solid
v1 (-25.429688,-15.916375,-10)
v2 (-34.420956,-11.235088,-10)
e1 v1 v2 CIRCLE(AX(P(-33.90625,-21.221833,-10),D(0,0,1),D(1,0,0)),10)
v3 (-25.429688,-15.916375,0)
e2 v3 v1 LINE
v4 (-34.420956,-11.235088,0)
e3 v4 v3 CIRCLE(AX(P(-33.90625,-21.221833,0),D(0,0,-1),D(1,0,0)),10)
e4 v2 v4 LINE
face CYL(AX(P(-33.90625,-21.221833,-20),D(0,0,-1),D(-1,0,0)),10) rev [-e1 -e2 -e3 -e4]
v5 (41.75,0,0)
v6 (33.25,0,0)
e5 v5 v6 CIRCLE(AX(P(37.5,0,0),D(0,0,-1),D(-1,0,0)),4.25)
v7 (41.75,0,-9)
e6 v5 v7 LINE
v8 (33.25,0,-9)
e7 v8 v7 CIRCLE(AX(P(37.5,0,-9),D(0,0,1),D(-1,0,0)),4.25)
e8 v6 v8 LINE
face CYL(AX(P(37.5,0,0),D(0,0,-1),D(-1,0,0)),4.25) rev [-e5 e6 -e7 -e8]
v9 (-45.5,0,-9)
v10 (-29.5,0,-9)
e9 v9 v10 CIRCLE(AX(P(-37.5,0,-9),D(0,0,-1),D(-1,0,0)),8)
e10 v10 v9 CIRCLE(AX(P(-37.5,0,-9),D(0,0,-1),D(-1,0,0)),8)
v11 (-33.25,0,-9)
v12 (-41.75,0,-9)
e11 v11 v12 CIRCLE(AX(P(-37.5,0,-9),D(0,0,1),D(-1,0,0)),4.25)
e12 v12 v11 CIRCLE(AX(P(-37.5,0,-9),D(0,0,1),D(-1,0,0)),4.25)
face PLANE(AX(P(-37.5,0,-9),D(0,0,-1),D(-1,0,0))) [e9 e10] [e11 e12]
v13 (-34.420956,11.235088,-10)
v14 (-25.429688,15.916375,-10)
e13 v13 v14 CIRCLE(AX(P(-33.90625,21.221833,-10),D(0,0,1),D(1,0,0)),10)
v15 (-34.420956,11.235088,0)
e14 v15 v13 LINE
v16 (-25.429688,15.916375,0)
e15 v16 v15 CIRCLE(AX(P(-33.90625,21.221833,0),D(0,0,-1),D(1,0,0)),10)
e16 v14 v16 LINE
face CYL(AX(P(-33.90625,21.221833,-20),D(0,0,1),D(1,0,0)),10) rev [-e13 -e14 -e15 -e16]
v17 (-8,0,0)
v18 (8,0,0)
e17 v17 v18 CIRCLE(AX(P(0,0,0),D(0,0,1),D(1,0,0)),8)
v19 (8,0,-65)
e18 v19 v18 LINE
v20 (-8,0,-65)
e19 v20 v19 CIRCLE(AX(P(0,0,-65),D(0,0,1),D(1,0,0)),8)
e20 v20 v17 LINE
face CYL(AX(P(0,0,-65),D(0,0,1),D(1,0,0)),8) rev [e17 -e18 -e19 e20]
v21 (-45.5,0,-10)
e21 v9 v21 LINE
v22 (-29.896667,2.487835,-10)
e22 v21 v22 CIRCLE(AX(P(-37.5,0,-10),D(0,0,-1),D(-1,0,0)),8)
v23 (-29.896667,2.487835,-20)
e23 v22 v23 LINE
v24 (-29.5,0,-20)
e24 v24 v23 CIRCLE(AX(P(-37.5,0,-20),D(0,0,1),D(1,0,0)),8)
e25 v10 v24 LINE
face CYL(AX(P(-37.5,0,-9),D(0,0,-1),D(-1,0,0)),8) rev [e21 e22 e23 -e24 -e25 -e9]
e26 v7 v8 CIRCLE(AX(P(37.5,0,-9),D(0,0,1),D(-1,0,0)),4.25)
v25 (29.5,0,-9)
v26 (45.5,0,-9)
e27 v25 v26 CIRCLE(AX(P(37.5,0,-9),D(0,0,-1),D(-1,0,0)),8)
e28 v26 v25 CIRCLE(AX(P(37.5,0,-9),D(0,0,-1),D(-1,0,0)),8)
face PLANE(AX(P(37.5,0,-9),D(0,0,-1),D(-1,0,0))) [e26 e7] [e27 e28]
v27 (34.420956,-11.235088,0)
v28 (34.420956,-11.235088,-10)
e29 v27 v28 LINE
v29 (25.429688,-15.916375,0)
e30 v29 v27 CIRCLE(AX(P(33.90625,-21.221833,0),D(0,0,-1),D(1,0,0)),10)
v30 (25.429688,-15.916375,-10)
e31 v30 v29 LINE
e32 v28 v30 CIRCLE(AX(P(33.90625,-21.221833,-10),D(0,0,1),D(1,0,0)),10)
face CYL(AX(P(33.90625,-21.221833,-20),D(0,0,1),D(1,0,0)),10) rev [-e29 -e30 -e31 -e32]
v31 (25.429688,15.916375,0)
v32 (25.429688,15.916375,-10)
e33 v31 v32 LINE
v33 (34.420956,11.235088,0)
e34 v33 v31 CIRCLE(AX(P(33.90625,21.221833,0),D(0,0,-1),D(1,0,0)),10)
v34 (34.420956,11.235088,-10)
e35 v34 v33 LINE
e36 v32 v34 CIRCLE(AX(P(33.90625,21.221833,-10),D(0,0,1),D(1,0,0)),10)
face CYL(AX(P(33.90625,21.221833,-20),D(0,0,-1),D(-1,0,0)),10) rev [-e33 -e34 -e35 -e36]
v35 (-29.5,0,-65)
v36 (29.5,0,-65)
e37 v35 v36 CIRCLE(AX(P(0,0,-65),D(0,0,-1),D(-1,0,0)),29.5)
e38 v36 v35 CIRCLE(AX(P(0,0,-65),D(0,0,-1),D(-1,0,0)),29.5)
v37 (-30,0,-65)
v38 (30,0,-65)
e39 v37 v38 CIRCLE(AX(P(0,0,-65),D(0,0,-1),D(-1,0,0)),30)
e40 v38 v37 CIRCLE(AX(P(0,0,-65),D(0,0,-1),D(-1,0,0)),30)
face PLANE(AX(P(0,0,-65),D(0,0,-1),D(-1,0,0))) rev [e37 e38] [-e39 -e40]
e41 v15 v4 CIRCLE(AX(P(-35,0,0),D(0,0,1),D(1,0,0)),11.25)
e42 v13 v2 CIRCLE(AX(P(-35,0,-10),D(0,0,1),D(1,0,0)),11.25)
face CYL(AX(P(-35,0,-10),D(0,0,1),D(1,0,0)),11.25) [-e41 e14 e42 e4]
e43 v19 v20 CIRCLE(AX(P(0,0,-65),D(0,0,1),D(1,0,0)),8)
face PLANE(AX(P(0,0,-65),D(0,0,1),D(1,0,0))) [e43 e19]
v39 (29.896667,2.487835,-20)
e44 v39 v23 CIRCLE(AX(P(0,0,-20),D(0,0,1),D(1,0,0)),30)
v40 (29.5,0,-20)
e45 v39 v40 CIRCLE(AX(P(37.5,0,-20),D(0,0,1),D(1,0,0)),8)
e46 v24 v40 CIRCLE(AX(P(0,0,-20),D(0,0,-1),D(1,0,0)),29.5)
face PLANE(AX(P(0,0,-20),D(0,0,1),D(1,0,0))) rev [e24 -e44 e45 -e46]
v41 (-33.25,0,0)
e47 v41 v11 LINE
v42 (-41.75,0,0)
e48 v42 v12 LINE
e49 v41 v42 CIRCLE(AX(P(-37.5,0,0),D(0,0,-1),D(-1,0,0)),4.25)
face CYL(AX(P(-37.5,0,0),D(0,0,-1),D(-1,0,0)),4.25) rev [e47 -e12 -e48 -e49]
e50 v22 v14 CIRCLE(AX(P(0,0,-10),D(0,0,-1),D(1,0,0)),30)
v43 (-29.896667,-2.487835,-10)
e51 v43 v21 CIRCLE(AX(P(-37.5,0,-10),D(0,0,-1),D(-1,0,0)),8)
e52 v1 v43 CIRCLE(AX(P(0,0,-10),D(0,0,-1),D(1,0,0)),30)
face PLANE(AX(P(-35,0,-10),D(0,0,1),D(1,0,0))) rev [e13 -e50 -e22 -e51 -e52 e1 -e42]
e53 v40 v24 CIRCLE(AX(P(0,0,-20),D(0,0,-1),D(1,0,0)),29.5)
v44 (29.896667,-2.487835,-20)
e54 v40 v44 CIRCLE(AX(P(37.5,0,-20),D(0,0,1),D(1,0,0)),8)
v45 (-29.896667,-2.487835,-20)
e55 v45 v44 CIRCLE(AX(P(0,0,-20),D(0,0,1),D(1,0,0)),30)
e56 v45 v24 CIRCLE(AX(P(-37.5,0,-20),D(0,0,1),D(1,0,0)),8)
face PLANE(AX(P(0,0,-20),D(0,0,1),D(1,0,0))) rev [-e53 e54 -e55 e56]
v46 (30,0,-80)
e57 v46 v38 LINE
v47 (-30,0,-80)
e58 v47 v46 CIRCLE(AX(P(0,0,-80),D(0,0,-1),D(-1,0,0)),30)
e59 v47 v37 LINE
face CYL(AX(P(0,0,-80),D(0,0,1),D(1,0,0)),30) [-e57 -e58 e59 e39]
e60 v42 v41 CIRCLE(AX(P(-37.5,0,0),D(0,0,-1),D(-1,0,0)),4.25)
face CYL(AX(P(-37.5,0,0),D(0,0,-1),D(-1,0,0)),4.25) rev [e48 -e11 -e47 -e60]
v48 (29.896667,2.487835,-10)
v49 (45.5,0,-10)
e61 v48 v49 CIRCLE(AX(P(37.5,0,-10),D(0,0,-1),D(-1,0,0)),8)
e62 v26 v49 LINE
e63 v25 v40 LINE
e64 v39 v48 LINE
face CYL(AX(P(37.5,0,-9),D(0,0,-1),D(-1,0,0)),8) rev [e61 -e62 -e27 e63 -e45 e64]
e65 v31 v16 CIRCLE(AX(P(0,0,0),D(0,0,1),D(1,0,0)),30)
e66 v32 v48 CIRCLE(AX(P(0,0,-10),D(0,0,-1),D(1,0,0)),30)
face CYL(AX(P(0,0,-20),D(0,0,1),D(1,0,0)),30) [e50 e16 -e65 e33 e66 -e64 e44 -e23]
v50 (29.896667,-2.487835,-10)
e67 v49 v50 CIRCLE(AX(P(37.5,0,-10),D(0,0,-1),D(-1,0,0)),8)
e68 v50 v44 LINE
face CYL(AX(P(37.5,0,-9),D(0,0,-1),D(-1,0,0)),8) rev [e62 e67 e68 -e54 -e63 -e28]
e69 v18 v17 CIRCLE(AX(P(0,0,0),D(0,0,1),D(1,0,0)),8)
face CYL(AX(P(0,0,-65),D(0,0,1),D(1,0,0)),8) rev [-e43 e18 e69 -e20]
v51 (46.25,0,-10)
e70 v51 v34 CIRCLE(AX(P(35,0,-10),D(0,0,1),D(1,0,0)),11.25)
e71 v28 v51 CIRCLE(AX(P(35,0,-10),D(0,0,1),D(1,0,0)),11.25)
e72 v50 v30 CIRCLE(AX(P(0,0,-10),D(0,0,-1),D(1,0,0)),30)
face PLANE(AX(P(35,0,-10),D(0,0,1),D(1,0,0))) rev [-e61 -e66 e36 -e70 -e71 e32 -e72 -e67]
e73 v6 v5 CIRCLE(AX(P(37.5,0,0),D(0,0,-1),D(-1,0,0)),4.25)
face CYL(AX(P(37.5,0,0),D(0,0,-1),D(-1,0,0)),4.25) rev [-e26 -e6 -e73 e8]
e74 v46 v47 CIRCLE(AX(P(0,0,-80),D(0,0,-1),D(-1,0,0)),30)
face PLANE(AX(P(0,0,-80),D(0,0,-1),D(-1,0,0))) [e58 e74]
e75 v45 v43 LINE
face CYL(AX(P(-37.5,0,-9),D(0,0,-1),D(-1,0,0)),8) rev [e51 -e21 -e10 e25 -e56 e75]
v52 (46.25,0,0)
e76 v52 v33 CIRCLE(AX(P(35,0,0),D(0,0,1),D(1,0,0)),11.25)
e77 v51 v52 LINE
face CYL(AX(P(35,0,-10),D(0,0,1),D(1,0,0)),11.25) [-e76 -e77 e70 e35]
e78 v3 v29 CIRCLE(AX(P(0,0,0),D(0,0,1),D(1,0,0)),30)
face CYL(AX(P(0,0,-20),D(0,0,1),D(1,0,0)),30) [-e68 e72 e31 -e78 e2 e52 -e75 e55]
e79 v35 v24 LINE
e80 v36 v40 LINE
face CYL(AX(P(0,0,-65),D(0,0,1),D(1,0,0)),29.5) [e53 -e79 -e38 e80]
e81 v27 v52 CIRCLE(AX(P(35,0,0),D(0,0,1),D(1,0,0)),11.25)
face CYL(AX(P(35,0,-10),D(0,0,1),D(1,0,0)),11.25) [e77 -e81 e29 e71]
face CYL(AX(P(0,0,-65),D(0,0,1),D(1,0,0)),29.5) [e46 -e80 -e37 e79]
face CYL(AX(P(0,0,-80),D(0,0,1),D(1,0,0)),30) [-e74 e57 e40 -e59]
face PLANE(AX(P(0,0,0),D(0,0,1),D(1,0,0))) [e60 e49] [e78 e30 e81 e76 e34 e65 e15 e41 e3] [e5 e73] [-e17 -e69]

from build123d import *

# Parameters (mm, degrees)
SKETCH1_R           = 30
BOSS_EXTRUDE1_DEPTH = 20
SKETCH2_R           = 29.5
BOSS_EXTRUDE2_DEPTH = 45
SKETCH3_R           = 30
BOSS_EXTRUDE3_DEPTH = 15
SKETCH4_R           = 8
CUT_EXTRUDE1_DEPTH  = 65
SKETCH5_R           = 11.25
BOSS_EXTRUDE4_DEPTH = 10
FILLET1_R           = 10
SKETCH6_R           = 4.25
CUT_EXTRUDE2_DEPTH  = 90.101417022
SKETCH_7_2_R        = 8
CUT_EXTRUDE3_DEPTH  = 1
CUT_EXTRUDE4_REACH  = 91.101
SKETCH_7_2_2_R      = 8


with BuildPart() as part:
    # Sketch1 → Boss-Extrude1 (new body)
    with BuildSketch(Plane.XY):
        Circle(SKETCH1_R)
    extrude(amount=-BOSS_EXTRUDE1_DEPTH)

    # Sketch2 → Boss-Extrude2 (add)
    with BuildSketch(Plane(origin=(0, 0, -20), x_dir=(-1, 0, 0), z_dir=(0, 0, -1))):
        with Locations(Location((0, 0, 0), (0, 0, 180))):
            Circle(SKETCH2_R)
    extrude(amount=BOSS_EXTRUDE2_DEPTH)

    # Sketch3 → Boss-Extrude3 (add)
    with BuildSketch(Plane(origin=(0, 0, -65), x_dir=(-1, 0, 0), z_dir=(0, 0, -1))):
        with Locations(Location((0, 0, 0), (0, 0, 180))):
            Circle(SKETCH3_R)
    extrude(amount=BOSS_EXTRUDE3_DEPTH)

    # Sketch4 → Cut-Extrude1 (cut)
    with BuildSketch(Plane.XY):
        Circle(SKETCH4_R)
    extrude(amount=-CUT_EXTRUDE1_DEPTH, mode=Mode.SUBTRACT)

    # Sketch5 → Boss-Extrude4 (add)
    with BuildSketch(Plane.XY):
        with Locations((35, 0)):
            Circle(SKETCH5_R)
        with Locations((-35, 0)):
            Circle(SKETCH5_R)
    extrude(amount=-BOSS_EXTRUDE4_DEPTH)

    # Fillet1
    fillet1_edges = [part.edges().sort_by_distance(p)[0] for p in [
        (28.549107143, 9.216750042, -5),
        (28.549107143, -9.216750042, -5),
        (-28.549107143, -9.216750042, -5),
        (-28.549107143, 9.216750042, -5),
    ]]
    fillet(fillet1_edges, radius=FILLET1_R)

    # Sketch6 → Cut-Extrude2 (cut, through all)
    with BuildSketch(Plane(origin=(0, 0, -10), x_dir=(-1, 0, 0), z_dir=(0, 0, -1))):
        with Locations((37.5, 0)):
            Circle(SKETCH6_R)
        with Locations((-37.5, 0)):
            Circle(SKETCH6_R)
    extrude(amount=-CUT_EXTRUDE2_DEPTH, mode=Mode.SUBTRACT)

    # Sketch 7_2 → Cut-Extrude3 (cut)
    with BuildSketch(Plane(origin=(0, 0, -10), x_dir=(-1, 0, 0), z_dir=(0, 0, -1))):
        with Locations((37.5, 0)):
            Circle(SKETCH_7_2_R)
        with Locations((-37.5, 0)):
            Circle(SKETCH_7_2_R)
    extrude(amount=-CUT_EXTRUDE3_DEPTH, mode=Mode.SUBTRACT)

    # Sketch 7_2 2 → Cut-Extrude4 (cut, up to next)
    with BuildSketch(Plane(origin=(0, 0, -10), x_dir=(-1, 0, 0), z_dir=(0, 0, -1)), mode=Mode.PRIVATE) as cut_extrude4_sk1:
        with Locations((37.5, 0)):
            Circle(SKETCH_7_2_2_R)
    cut_extrude4_tool1 = extrude(cut_extrude4_sk1.sketch, amount=CUT_EXTRUDE4_REACH, mode=Mode.PRIVATE) & part.part
    # Sketch 7_2 2 → Cut-Extrude4 (cut, up to next)
    with BuildSketch(Plane(origin=(0, 0, -10), x_dir=(-1, 0, 0), z_dir=(0, 0, -1)), mode=Mode.PRIVATE) as cut_extrude4_sk2:
        with Locations((-37.5, 0)):
            Circle(SKETCH_7_2_2_R)
    cut_extrude4_tool2 = extrude(cut_extrude4_sk2.sketch, amount=CUT_EXTRUDE4_REACH, mode=Mode.PRIVATE) & part.part
    add(cut_extrude4_tool1.solids().sort_by_distance((-37.5, 0, -10))[0], mode=Mode.SUBTRACT)
    add(cut_extrude4_tool2.solids().sort_by_distance((37.5, 0, -10))[0], mode=Mode.SUBTRACT)


solid = part.part
